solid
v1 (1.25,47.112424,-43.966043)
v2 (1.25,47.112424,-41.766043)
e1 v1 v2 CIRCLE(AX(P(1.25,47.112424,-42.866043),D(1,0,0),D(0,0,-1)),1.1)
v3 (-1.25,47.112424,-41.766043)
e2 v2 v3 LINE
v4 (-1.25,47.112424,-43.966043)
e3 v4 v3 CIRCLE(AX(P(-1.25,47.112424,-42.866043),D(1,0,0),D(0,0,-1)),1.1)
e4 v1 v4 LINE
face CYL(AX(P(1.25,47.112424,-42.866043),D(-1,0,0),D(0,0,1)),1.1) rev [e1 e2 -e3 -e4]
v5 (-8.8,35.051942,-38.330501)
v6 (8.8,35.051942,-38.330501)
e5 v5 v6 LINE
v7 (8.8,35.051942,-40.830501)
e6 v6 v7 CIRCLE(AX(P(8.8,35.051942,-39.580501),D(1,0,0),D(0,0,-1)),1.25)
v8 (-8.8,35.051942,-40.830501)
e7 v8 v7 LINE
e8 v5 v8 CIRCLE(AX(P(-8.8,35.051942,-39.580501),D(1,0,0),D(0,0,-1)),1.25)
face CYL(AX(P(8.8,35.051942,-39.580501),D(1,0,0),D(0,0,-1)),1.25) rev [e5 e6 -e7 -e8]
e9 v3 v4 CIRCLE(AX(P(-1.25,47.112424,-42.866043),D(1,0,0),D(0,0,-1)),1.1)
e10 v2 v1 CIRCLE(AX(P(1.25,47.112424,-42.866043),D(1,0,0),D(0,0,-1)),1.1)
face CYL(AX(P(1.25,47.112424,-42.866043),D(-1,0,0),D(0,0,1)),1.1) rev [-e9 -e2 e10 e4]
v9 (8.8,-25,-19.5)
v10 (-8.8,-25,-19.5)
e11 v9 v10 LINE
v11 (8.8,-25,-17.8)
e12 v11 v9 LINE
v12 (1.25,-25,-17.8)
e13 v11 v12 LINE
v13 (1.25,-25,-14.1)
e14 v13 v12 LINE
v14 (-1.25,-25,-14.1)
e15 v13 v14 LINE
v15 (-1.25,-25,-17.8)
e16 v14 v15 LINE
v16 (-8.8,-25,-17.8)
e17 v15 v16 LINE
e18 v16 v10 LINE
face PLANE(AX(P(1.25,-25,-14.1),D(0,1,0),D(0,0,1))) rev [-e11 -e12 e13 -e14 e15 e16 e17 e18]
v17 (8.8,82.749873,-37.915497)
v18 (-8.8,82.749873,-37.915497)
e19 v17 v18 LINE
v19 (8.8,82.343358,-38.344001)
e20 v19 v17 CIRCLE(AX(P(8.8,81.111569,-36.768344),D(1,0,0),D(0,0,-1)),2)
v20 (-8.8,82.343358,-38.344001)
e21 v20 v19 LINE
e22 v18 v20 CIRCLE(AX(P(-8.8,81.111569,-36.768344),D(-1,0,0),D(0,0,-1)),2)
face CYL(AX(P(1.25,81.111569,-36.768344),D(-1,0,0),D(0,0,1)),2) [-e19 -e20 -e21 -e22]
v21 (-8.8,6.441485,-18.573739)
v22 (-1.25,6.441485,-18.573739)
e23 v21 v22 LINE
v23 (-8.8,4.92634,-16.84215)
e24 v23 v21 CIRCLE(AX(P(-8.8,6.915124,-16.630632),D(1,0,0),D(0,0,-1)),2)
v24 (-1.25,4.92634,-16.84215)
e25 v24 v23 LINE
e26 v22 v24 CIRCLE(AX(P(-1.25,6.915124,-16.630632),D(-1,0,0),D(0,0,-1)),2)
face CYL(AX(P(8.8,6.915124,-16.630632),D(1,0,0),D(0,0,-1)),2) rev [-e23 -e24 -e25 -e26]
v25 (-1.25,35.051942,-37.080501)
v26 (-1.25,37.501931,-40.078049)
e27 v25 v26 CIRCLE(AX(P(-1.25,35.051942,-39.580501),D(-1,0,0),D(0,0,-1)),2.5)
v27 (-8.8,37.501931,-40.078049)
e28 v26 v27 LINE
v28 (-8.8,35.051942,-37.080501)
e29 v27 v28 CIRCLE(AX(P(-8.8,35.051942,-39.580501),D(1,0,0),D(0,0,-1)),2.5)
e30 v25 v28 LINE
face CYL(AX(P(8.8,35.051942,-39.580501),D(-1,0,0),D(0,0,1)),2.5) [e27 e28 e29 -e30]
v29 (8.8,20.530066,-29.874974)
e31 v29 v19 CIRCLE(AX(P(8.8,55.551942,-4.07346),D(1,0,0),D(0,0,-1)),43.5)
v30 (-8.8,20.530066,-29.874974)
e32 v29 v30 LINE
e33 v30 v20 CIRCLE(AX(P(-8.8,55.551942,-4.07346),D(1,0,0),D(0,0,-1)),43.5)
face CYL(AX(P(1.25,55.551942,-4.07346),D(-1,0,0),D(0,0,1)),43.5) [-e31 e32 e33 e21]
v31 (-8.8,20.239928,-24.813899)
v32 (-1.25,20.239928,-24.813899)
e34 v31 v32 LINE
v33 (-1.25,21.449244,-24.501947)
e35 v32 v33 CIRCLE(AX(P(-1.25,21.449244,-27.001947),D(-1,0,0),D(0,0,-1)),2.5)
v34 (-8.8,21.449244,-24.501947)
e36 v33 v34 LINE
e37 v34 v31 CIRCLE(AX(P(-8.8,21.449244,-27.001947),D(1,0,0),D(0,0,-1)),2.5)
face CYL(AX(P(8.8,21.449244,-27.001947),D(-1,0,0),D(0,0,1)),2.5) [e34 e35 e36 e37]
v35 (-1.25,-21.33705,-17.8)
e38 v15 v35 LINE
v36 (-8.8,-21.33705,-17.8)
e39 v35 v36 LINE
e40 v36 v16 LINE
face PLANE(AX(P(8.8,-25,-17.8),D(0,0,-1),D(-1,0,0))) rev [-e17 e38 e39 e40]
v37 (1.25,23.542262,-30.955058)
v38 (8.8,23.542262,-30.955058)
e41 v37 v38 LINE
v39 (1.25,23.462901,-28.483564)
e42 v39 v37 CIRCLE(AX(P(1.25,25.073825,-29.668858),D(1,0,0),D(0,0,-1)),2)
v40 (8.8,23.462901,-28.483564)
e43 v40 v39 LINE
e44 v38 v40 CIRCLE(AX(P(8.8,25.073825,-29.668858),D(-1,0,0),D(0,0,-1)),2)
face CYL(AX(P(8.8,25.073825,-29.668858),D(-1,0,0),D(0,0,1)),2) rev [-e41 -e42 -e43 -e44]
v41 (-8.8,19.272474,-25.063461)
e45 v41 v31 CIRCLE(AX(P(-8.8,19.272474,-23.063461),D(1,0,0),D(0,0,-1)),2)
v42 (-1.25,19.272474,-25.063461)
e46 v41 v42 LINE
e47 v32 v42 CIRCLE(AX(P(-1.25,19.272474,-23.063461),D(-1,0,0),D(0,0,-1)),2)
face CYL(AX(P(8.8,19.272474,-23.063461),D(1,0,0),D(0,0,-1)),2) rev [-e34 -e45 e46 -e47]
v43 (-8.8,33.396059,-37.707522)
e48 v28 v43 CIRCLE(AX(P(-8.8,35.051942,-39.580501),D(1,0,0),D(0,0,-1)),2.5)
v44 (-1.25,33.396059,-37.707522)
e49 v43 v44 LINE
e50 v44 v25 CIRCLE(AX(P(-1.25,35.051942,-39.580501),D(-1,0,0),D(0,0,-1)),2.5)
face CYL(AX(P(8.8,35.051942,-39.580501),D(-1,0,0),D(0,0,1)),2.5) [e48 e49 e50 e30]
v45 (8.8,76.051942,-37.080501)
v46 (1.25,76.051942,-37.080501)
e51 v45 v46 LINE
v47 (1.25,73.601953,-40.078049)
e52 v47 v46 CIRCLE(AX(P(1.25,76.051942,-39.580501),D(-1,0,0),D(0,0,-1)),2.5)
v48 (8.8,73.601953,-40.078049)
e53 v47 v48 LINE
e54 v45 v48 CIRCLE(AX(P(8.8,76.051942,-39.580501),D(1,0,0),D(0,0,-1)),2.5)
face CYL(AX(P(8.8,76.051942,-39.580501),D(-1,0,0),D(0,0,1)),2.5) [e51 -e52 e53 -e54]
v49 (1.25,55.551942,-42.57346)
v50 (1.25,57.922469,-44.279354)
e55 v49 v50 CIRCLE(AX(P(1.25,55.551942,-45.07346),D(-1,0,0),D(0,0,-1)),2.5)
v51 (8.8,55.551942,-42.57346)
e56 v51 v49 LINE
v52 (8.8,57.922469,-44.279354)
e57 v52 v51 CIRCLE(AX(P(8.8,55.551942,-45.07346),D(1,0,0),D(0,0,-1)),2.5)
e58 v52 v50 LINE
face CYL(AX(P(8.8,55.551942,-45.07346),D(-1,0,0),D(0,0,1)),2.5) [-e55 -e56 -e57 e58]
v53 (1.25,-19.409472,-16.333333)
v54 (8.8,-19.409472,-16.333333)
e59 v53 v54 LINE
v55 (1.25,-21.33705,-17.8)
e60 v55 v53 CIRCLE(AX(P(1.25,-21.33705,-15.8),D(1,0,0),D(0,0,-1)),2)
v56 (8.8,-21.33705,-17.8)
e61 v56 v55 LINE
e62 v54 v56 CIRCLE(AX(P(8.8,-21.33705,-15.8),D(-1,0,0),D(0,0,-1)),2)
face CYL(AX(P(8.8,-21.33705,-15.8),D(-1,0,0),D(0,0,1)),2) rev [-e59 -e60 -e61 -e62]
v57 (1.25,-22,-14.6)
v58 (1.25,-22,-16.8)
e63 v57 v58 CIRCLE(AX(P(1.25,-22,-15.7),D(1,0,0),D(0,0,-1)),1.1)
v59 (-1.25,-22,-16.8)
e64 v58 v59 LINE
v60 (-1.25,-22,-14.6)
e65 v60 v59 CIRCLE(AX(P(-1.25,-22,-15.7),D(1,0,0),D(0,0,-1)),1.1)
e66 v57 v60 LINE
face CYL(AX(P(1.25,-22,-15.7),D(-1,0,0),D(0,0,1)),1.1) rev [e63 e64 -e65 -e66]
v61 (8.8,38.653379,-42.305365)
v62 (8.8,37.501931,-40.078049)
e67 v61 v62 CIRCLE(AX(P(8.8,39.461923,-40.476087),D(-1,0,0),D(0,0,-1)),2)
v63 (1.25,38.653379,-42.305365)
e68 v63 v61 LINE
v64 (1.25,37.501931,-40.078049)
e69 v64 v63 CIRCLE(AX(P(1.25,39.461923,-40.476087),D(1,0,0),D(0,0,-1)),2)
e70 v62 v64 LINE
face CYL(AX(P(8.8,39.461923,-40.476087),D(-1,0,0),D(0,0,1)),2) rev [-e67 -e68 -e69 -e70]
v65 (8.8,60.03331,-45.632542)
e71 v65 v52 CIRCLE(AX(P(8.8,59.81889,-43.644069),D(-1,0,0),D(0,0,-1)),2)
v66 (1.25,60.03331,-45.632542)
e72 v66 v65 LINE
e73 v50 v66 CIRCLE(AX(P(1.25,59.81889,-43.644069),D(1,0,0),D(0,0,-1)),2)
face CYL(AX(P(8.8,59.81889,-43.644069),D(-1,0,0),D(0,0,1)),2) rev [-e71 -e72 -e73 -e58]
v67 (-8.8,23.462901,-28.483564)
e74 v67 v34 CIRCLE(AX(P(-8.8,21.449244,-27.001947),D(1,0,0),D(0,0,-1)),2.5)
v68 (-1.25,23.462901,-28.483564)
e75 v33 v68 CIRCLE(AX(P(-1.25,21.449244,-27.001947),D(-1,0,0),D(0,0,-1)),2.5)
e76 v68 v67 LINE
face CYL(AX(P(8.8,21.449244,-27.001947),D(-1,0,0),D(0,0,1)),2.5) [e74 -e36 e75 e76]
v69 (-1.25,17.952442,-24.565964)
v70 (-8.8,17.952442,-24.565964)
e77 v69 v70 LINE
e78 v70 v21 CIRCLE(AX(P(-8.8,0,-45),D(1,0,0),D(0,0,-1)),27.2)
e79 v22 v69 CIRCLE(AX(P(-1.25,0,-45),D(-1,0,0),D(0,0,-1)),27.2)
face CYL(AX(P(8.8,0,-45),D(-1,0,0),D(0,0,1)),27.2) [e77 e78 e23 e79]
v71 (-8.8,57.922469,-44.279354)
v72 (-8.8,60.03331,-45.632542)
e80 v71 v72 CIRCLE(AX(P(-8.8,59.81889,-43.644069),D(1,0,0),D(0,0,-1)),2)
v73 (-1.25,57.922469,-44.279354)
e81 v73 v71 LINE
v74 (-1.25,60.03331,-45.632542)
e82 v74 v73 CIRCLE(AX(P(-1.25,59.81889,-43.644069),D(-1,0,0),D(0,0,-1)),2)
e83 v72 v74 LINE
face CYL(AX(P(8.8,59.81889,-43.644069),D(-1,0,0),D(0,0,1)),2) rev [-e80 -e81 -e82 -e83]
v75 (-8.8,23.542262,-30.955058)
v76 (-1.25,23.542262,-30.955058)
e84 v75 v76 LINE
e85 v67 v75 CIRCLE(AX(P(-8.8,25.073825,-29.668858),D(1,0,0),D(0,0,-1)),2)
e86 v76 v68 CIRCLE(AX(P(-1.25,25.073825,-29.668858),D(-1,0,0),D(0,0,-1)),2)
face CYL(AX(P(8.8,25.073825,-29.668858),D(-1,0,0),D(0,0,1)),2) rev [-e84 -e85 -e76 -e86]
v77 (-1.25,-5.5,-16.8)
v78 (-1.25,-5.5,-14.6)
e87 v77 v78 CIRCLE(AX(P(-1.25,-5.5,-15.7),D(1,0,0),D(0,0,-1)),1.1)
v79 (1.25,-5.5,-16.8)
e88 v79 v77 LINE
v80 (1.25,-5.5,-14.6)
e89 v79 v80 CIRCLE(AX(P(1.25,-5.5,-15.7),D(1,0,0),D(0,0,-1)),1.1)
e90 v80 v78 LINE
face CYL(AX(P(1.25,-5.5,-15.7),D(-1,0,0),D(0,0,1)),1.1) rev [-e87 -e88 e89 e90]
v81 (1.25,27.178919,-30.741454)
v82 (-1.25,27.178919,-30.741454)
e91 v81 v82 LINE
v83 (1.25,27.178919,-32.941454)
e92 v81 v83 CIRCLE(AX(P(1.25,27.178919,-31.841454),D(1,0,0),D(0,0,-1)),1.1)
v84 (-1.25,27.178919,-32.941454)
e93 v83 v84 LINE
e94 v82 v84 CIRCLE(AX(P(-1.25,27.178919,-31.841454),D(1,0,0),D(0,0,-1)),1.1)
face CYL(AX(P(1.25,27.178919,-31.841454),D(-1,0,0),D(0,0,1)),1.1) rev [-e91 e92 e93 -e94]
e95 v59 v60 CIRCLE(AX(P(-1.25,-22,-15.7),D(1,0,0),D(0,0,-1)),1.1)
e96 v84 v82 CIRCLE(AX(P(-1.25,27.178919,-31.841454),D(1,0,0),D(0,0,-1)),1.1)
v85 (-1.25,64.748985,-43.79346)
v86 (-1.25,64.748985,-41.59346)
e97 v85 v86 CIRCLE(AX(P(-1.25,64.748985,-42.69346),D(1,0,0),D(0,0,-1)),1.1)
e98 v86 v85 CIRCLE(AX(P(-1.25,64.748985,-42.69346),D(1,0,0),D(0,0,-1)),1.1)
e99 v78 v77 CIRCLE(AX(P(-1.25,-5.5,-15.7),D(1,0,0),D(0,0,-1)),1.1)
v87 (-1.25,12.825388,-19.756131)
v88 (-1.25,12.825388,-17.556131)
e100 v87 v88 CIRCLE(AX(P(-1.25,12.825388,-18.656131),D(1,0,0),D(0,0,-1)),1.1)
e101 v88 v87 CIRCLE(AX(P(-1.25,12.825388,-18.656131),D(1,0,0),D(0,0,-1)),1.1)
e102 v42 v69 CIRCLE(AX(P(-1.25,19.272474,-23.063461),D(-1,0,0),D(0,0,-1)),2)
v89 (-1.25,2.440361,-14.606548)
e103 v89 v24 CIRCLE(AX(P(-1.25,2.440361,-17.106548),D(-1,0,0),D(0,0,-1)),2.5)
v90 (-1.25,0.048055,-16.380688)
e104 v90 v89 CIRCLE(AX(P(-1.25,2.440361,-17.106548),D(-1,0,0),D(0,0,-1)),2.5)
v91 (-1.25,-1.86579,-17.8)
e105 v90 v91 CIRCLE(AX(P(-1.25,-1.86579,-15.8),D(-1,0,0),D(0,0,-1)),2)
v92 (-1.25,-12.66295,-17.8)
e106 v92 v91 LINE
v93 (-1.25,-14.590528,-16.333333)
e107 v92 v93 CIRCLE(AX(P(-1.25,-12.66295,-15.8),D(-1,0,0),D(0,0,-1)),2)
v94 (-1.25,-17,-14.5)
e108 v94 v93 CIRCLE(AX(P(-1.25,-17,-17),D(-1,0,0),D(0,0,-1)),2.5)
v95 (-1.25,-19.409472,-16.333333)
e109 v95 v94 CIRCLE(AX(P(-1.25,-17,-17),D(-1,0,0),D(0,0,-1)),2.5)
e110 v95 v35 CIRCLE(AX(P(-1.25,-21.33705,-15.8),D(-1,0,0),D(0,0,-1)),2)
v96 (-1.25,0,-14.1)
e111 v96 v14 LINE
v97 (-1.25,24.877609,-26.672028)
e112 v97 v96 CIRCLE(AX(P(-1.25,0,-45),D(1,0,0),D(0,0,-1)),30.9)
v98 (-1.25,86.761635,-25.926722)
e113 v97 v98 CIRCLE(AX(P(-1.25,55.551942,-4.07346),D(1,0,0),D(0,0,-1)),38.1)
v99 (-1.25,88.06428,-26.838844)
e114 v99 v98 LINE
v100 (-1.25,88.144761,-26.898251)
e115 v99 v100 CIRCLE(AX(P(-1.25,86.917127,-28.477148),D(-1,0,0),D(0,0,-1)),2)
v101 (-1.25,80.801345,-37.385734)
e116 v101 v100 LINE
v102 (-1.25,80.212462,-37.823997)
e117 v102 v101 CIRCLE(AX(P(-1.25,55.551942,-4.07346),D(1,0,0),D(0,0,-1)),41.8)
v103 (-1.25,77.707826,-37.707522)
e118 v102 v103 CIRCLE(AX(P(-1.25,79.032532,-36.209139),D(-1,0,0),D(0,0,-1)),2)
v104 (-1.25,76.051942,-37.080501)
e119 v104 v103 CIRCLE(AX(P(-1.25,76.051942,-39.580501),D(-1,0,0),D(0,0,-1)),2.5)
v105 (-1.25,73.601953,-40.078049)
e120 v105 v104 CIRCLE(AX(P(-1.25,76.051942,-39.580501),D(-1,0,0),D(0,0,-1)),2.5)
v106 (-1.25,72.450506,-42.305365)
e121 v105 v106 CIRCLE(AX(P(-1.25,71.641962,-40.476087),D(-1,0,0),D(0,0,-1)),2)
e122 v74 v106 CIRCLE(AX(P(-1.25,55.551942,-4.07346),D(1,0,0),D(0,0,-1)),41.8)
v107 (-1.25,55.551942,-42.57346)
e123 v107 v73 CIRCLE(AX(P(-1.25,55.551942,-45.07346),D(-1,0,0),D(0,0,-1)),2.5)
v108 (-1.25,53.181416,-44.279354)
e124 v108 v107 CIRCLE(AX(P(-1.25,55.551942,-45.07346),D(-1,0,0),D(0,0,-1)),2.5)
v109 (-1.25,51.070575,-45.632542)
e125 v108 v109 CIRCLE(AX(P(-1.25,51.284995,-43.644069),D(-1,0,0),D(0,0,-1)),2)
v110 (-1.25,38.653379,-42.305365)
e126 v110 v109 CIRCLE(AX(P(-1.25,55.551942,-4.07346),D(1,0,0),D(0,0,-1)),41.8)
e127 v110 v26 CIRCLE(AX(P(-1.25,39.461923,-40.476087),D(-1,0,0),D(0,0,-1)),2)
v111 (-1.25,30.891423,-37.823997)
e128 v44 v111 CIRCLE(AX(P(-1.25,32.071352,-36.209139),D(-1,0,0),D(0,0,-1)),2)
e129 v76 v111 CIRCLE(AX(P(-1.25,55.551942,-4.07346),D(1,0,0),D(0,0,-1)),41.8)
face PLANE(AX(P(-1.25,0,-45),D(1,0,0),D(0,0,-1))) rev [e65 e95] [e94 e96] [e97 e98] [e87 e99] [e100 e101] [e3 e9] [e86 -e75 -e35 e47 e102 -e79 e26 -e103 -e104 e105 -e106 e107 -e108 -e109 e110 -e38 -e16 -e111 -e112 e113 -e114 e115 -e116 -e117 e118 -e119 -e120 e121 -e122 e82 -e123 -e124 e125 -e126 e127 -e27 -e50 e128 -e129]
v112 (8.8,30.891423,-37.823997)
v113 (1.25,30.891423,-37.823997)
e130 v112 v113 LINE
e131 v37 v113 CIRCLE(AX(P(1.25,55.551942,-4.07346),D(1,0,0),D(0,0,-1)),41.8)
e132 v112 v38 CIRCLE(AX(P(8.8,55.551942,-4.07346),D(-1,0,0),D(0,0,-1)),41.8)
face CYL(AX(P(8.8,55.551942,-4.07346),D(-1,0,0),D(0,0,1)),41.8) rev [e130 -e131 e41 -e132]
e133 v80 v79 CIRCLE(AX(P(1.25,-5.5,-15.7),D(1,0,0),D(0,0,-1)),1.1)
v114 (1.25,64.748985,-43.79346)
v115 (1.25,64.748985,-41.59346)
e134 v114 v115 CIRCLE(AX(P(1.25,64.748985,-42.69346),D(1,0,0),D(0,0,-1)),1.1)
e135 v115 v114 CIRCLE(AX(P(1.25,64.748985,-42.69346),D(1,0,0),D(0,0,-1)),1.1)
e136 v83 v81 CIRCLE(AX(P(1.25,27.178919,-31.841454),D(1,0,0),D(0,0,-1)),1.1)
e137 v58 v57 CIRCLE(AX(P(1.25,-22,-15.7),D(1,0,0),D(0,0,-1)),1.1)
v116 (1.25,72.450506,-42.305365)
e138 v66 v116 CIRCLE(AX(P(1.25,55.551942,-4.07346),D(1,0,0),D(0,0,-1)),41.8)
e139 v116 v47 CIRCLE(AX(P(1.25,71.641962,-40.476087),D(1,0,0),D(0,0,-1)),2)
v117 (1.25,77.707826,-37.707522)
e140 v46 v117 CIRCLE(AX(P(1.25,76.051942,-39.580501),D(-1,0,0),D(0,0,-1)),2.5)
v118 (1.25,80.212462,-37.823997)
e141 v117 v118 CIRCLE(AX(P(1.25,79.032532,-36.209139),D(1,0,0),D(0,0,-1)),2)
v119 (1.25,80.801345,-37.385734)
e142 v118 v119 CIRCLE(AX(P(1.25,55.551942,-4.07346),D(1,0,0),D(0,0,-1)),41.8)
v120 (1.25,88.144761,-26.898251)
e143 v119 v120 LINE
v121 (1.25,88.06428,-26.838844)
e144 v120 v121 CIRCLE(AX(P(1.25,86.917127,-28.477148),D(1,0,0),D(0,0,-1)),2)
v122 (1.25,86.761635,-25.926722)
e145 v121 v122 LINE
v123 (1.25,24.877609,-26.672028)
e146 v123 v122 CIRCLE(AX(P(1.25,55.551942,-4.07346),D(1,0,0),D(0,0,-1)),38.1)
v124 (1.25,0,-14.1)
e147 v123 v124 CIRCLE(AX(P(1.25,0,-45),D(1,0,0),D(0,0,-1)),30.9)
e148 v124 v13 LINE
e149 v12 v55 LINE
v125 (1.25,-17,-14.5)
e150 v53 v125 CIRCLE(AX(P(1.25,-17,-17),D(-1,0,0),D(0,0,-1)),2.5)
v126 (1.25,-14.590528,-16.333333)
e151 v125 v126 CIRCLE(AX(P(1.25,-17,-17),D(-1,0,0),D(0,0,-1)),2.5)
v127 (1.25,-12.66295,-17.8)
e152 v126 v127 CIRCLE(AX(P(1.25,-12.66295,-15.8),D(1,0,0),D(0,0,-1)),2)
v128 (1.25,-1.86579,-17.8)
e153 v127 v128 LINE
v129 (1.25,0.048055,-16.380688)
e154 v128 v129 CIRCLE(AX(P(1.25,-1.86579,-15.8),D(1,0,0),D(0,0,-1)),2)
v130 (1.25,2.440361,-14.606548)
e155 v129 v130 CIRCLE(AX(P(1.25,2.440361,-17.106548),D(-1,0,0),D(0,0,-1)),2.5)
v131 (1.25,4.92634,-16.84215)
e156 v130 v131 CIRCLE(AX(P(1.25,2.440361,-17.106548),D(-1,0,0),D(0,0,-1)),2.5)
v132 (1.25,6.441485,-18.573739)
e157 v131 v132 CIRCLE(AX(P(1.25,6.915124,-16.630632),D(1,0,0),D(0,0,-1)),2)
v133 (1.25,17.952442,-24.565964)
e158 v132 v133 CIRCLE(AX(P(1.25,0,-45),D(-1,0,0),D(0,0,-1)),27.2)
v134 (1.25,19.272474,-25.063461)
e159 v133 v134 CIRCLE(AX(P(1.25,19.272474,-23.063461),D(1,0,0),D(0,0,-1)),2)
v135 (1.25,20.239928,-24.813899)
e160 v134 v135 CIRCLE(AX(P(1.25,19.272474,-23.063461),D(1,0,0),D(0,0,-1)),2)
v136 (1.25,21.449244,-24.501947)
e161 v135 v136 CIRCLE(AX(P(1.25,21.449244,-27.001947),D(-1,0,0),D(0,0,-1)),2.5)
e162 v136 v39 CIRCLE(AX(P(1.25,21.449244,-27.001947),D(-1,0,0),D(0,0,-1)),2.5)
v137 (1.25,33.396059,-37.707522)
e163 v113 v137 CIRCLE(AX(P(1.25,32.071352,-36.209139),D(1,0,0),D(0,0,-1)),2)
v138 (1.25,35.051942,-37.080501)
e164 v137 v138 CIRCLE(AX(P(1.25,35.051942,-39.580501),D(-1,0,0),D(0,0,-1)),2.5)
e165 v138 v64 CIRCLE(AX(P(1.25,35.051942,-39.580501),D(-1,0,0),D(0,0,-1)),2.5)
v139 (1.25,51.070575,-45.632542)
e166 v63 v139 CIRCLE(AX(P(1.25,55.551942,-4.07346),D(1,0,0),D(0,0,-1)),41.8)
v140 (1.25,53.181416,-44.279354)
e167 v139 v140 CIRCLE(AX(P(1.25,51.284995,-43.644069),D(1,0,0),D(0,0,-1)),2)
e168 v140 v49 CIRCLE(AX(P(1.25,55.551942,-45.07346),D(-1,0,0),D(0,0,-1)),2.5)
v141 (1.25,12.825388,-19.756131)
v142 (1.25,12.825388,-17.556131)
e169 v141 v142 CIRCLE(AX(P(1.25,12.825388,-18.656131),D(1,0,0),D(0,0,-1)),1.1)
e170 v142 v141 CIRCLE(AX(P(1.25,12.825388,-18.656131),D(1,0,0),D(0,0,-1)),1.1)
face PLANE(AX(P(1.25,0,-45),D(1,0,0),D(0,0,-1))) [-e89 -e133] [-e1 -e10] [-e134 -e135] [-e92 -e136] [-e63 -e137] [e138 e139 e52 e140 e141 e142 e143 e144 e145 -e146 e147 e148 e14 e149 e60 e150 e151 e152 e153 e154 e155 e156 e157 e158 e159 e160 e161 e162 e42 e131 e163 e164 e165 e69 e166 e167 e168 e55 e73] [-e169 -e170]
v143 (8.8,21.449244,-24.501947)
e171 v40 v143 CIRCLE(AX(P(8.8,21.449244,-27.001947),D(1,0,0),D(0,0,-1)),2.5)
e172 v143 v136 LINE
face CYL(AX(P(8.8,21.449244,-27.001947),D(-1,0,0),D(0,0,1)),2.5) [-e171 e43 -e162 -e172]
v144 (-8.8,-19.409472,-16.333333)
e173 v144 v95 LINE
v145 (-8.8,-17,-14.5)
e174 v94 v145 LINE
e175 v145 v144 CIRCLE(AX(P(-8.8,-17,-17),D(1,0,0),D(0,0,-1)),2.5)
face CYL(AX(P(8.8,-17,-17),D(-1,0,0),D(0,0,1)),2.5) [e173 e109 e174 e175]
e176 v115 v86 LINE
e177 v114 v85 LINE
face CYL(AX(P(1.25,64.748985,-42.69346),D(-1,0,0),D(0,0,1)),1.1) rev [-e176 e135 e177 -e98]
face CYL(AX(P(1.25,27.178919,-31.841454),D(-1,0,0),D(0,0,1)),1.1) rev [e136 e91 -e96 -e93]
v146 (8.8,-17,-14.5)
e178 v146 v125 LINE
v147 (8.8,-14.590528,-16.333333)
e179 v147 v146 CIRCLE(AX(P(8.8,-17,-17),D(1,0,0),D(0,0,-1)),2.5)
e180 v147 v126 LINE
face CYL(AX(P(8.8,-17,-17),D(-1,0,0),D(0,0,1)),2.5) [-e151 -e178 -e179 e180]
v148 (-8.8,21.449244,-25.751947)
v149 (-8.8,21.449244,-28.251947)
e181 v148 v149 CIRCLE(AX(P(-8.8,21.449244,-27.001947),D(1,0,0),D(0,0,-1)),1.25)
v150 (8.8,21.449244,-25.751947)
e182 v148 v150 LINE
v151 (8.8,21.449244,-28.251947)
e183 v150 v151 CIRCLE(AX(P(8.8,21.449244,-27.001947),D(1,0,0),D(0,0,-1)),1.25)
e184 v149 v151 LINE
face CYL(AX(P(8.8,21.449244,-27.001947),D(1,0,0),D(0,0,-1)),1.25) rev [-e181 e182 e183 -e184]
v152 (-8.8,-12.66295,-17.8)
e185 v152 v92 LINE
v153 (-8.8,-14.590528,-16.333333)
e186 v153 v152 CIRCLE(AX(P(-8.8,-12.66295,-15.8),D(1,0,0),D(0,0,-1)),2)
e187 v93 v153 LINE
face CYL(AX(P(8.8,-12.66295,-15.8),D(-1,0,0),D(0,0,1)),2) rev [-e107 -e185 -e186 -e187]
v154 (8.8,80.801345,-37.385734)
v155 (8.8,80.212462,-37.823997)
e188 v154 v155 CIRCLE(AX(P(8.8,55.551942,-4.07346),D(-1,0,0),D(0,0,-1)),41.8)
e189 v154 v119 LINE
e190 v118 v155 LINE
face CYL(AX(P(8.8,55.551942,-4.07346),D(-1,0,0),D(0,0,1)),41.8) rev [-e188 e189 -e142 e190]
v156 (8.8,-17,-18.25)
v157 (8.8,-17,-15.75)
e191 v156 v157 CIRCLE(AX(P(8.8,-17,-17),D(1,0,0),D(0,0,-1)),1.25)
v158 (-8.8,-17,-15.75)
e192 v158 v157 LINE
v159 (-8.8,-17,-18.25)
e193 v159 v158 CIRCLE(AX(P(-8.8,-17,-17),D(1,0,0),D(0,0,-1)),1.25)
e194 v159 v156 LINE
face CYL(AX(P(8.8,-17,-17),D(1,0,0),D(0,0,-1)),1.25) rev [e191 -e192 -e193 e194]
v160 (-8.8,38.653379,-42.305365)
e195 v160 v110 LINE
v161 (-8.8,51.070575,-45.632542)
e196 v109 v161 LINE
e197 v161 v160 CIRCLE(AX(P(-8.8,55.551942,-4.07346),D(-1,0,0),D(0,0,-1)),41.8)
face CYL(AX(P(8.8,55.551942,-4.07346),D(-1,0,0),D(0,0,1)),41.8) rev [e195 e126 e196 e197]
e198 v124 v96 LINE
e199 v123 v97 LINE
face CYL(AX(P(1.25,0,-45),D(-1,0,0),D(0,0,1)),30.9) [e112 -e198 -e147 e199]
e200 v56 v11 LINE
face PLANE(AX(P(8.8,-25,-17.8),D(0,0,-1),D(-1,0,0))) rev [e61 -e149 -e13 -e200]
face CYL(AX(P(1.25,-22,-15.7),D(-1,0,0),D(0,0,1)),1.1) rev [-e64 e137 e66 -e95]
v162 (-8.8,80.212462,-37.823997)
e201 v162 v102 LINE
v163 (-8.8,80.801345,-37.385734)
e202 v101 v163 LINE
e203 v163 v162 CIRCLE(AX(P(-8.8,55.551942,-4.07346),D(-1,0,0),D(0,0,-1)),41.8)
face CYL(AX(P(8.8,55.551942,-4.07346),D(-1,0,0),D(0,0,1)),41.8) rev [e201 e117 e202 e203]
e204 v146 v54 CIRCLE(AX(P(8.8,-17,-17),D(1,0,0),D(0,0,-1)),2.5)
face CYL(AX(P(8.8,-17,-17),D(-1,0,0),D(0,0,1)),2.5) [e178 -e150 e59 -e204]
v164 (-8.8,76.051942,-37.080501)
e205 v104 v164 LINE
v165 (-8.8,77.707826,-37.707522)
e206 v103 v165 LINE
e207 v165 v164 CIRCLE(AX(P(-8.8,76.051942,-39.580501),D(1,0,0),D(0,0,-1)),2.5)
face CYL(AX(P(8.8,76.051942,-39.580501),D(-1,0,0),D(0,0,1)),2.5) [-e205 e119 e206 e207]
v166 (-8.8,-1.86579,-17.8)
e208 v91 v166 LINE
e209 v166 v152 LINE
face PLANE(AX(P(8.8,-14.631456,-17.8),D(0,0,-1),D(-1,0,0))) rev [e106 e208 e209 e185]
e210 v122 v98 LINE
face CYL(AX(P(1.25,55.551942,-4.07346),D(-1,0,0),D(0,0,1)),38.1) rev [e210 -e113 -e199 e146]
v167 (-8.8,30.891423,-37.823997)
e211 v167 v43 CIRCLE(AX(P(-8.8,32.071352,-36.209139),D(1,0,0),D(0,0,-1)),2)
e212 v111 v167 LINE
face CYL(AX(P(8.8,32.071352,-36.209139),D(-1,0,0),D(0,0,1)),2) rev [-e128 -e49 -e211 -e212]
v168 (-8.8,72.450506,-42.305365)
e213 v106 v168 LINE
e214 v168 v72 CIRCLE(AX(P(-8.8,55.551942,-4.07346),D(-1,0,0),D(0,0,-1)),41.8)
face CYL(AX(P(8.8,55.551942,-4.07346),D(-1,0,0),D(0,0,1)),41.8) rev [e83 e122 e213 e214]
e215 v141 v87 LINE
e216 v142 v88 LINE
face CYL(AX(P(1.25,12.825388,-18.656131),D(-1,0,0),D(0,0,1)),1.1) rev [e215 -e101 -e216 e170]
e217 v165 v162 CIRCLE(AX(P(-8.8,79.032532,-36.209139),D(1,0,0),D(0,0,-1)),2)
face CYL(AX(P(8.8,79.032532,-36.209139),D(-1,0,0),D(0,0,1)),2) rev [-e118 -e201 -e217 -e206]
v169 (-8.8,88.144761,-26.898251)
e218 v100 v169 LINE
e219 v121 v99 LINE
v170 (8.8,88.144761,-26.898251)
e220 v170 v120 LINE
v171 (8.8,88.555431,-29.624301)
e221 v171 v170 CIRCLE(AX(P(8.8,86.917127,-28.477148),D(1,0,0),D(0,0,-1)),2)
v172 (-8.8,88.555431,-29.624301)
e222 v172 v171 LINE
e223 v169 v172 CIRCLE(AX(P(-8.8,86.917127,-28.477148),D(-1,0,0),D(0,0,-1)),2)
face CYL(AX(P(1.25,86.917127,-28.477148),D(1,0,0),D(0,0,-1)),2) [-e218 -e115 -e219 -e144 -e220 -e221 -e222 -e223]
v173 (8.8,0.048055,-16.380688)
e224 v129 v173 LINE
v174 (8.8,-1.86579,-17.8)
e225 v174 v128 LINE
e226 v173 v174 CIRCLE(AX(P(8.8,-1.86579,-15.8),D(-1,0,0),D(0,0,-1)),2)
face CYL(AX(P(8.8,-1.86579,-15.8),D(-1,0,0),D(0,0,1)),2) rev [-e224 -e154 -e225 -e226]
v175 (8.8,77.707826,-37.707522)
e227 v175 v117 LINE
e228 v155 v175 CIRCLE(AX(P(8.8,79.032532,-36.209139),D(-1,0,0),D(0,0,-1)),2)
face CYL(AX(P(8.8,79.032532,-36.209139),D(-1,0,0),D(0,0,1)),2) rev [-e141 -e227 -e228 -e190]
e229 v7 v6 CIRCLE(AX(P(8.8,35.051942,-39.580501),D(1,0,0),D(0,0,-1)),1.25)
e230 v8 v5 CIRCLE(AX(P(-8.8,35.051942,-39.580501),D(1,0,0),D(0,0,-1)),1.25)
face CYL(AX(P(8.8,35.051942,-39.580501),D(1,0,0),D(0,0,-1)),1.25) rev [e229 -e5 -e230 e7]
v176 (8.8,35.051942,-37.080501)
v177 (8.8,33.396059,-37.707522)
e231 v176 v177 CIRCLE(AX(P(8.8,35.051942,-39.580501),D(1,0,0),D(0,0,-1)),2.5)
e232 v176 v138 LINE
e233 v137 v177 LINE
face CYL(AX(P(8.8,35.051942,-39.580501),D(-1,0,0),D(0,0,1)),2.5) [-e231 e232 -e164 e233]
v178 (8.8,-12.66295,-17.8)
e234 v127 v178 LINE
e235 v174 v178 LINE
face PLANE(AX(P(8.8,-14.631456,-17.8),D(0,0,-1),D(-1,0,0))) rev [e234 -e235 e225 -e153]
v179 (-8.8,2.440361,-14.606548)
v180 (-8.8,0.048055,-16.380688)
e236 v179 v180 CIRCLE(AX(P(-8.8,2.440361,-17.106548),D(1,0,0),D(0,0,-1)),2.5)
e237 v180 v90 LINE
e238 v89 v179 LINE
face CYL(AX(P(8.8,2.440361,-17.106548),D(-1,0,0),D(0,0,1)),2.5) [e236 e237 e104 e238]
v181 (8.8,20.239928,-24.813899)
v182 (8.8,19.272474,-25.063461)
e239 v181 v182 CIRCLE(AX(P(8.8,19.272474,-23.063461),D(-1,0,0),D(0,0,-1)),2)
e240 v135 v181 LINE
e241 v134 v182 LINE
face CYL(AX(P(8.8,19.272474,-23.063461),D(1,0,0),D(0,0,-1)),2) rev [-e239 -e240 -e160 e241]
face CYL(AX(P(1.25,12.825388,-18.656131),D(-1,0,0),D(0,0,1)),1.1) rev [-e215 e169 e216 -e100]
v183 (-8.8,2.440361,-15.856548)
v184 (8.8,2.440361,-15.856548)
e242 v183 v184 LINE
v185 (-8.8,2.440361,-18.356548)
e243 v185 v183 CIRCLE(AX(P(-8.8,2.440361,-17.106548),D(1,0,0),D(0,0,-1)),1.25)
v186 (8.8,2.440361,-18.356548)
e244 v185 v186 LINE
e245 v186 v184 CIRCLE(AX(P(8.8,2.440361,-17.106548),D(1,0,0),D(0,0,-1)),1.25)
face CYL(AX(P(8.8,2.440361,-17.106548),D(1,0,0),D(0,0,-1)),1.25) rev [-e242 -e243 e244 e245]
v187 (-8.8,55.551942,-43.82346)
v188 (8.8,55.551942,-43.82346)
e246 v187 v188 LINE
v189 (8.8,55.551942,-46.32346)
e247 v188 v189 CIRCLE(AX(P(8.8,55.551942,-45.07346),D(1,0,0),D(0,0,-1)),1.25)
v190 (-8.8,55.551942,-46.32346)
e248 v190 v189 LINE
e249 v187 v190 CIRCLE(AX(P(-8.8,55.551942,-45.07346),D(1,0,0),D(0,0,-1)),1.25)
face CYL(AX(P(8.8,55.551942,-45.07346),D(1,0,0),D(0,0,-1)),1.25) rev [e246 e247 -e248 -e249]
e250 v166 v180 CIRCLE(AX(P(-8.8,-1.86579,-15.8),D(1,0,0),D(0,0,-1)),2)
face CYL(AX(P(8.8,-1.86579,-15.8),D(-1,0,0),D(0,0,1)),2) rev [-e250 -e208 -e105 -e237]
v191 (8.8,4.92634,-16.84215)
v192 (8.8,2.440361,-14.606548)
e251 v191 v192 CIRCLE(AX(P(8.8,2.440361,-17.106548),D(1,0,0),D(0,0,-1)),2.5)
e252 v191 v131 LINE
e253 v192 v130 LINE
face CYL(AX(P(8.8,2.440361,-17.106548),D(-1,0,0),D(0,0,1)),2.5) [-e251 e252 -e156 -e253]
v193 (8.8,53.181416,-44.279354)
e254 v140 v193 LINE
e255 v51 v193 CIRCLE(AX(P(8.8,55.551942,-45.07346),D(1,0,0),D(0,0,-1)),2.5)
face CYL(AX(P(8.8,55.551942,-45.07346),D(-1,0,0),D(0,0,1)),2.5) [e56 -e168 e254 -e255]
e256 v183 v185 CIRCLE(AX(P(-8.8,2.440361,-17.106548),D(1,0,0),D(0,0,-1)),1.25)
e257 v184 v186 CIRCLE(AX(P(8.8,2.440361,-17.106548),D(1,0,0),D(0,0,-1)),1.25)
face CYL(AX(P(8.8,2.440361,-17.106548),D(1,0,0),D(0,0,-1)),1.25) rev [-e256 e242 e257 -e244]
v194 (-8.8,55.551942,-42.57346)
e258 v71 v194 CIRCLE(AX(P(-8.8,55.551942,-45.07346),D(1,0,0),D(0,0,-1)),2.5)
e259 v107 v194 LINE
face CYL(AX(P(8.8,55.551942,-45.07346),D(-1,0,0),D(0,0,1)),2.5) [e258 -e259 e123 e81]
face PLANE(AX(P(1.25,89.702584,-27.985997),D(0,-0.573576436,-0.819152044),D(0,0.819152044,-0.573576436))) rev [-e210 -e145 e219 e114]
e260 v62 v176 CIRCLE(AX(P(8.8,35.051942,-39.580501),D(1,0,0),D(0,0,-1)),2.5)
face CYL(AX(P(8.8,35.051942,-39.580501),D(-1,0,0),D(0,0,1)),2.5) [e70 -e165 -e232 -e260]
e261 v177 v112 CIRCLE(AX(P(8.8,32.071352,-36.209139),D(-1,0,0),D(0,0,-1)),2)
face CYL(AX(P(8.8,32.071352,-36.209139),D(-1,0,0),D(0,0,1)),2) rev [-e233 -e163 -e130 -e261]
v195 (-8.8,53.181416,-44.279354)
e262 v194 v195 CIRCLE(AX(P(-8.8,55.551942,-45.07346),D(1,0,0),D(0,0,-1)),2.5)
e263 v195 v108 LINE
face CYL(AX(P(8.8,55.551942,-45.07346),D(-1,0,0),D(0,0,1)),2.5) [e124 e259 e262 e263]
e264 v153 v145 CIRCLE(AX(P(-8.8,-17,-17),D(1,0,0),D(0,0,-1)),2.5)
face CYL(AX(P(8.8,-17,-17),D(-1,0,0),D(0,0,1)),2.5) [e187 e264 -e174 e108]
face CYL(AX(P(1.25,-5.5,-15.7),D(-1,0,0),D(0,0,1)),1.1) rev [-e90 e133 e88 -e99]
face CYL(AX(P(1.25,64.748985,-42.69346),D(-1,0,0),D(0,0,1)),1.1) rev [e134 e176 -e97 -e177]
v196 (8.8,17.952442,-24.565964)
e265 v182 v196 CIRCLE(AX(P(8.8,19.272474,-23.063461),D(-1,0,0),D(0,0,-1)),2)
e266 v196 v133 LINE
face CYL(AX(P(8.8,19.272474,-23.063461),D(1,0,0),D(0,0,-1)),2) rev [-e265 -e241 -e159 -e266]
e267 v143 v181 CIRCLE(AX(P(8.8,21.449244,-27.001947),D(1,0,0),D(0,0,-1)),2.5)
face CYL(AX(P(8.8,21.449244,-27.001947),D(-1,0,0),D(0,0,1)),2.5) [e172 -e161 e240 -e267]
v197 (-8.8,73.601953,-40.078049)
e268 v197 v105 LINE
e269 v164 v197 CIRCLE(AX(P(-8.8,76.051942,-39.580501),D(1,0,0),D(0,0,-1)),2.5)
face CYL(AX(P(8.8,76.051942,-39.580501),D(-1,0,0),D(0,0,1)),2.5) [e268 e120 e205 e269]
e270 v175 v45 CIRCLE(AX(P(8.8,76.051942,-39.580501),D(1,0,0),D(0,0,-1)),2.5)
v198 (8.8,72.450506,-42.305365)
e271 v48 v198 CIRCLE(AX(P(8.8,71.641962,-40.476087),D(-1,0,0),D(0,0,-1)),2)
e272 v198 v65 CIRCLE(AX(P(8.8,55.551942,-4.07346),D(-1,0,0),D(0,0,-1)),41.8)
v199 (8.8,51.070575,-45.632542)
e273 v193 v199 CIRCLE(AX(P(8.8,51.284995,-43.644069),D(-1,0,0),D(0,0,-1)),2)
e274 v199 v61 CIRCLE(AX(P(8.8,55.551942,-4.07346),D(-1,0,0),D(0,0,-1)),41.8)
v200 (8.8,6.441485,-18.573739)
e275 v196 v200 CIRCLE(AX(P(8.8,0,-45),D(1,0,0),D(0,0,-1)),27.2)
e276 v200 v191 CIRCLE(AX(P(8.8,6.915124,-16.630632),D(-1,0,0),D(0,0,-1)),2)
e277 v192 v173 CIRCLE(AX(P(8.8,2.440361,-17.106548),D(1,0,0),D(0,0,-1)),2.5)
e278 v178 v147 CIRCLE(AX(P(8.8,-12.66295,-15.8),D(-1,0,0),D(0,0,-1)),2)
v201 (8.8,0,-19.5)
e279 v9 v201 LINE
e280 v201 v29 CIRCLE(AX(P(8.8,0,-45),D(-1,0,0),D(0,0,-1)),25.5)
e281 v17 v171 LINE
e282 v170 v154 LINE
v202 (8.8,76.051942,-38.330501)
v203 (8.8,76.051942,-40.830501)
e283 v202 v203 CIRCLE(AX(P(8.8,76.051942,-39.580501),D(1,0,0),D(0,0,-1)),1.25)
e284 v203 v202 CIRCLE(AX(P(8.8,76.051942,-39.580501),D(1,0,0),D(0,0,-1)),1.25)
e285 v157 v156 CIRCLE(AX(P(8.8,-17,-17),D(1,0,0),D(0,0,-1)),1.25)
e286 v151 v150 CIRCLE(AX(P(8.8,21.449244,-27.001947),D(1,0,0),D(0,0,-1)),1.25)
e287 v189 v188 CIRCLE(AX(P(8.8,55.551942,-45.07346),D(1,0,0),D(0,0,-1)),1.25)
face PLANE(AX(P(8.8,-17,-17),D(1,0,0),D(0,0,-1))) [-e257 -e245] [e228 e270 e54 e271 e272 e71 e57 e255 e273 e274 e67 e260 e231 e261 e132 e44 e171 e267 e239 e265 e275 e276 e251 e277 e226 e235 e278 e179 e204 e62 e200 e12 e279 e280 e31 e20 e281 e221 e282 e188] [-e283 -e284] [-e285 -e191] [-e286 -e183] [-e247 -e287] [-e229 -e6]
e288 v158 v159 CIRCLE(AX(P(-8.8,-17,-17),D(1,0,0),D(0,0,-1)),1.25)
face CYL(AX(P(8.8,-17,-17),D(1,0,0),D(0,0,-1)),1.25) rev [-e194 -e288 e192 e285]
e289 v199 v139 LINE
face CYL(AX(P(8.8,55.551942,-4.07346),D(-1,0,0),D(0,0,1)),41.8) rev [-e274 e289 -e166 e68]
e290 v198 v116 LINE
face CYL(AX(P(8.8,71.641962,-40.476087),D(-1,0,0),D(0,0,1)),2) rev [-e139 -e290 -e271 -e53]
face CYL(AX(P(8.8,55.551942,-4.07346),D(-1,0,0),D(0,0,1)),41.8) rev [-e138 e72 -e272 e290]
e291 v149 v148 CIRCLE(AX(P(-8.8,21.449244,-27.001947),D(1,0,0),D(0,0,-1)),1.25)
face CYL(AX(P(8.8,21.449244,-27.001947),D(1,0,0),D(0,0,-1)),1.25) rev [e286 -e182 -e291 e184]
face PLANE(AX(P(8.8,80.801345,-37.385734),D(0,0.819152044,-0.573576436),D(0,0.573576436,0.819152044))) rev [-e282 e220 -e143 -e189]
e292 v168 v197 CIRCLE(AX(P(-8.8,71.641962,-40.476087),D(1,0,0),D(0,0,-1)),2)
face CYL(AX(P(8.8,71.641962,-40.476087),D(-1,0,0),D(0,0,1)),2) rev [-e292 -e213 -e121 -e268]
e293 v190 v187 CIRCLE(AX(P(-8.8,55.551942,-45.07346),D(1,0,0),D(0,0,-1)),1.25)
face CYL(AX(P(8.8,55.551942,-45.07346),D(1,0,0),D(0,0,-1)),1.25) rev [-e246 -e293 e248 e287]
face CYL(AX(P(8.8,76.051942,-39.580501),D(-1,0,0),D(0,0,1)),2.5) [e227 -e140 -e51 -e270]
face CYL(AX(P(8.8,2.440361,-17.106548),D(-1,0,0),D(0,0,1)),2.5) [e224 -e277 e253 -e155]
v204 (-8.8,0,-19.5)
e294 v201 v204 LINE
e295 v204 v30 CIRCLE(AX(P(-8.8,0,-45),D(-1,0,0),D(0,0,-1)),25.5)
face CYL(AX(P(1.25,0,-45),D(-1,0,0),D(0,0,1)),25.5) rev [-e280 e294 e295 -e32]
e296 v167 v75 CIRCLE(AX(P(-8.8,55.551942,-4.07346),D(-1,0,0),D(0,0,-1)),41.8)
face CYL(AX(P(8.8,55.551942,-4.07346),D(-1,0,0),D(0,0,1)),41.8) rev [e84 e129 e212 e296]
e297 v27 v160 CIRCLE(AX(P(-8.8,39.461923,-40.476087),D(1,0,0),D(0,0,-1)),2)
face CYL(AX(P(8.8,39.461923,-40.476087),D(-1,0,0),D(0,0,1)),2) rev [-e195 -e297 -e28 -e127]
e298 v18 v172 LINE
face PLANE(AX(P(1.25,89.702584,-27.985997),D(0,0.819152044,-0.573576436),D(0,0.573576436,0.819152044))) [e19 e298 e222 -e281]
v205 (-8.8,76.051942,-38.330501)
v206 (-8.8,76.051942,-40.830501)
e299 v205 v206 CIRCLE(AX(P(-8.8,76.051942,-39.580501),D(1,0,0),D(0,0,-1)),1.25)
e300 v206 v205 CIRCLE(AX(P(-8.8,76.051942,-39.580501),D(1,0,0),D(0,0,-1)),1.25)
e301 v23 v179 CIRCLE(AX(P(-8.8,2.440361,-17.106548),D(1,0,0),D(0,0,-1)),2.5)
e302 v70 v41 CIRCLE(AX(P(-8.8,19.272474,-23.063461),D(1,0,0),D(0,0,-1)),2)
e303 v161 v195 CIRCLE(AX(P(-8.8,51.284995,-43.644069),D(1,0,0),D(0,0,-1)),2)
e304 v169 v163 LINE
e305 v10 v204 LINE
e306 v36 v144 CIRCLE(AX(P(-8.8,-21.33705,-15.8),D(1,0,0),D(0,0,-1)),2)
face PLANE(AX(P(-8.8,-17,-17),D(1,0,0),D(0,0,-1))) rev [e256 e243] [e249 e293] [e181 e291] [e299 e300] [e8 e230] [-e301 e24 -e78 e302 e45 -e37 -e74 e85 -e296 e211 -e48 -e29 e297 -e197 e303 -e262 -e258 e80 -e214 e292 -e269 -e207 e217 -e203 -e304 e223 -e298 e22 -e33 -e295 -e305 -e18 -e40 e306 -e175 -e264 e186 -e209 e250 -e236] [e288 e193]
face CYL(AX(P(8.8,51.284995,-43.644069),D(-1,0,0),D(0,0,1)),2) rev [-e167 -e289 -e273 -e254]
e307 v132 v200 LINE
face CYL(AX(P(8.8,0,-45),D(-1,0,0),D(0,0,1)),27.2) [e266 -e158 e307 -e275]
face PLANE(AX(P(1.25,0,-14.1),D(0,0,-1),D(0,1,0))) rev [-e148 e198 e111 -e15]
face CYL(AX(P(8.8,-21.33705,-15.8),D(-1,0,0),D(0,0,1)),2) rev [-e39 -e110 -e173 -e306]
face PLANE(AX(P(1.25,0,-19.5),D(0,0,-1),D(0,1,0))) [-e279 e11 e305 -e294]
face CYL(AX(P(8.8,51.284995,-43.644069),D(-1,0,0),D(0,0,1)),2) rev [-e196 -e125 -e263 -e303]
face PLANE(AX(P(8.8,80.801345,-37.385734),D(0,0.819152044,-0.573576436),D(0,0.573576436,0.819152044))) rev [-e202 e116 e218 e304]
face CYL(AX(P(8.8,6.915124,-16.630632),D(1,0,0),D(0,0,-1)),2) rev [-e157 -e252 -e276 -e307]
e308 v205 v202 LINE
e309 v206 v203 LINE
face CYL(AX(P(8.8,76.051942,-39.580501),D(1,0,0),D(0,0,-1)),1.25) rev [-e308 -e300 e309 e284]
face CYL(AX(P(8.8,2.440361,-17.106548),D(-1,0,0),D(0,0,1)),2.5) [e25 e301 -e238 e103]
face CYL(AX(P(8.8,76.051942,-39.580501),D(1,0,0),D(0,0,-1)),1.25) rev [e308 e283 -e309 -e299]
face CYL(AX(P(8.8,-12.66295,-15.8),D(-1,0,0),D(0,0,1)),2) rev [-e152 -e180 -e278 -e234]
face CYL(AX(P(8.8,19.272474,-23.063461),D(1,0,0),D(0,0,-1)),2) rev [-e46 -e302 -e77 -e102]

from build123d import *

# Parameters (mm, degrees)
SKETCH_3_R         = 1.0999999999999992
SKETCH_3_R_2       = 1.100000000000007
SKETCH_3_R_3       = 1.0999999999999983
EXTRUDE_1_DEPTH    = 1.25
EXTRUDE_2_DEPTH    = 8.8
HOLE_WIZARD_M3_1_D = 2.5
FILLET_R2_1_R      = 2


with BuildPart() as part:
    # 草图3 → 凸台-拉伸1 (new, symmetric)
    with BuildSketch(Plane(origin=(0, 0, 0), x_dir=(0, 0, -1), z_dir=(1, 0, 0))):
        with BuildLine():
            Line((19.5, -3.12e-15), (19.500000000000004, -25.00000000000001))
            Line((19.500000000000004, -25.00000000000001), (14.100000000000005, -25.00000000000001))
            Line((14.100000000000005, -25.00000000000001), (14.100000000000001, 0))
            ThreePointArc((14.100000000000001, 0), (17.421526991333195, 13.936923136411288), (26.672027605840533, 24.877608967079777))
            ThreePointArc((26.672027605840533, 24.877608967079777), (42.17069683857236, 56.010769758457506), (25.926721927337365, 86.76163524108378))
            Line((25.926721927337365, 86.76163524108378), (27.985996640623934, 89.70258431819843))
            Line((27.985996640623934, 89.70258431819843), (38.157154957885716, 82.58066259212733))
            ThreePointArc((38.157154957885716, 82.58066259212733), (47.19107481579925, 49.796834454639864), (29.874974237829562, 20.530065652444478))
            ThreePointArc((29.874974237829562, 20.530065652444478), (22.241065963721567, 11.501344335873394), (19.5, -3.12e-15))
        make_face()
        with Locations((15.700000000000003, -22.000000000000014)):
            Circle(SKETCH_3_R, mode=Mode.SUBTRACT)
        with Locations((15.700000000000003, -5.5000000000000115)):
            Circle(SKETCH_3_R, mode=Mode.SUBTRACT)
        with Locations((18.656131284605202, 12.825388146408793)):
            Circle(SKETCH_3_R, mode=Mode.SUBTRACT)
        with Locations((42.69345970236235, 64.74898535672597)):
            Circle(SKETCH_3_R_2, mode=Mode.SUBTRACT)
        with Locations((31.841454389394453, 27.178918703364943)):
            Circle(SKETCH_3_R, mode=Mode.SUBTRACT)
        with Locations((42.86604311676676, 47.112423881836435)):
            Circle(SKETCH_3_R_3, mode=Mode.SUBTRACT)
    extrude(amount=EXTRUDE_1_DEPTH, both=True)

    # 草图4 → 凸台-拉伸2 (add, symmetric)
    with BuildSketch(Plane(origin=(0, 0, 0), x_dir=(0, 0, -1), z_dir=(1, 0, 0))):
        with BuildLine():
            Line((19.500000000000004, 3.12e-15), (19.500000000000004, -25.00000000000001))
            Line((19.500000000000004, -25.00000000000001), (17.800000000000004, -25.00000000000001))
            Line((17.800000000000004, -25.00000000000001), (17.800000000000004, -19.368543856465415))
            ThreePointArc((17.800000000000004, -19.368543856465415), (14.5, -17.00000000000001), (17.800000000000004, -14.63145614353461))
            Line((17.800000000000004, -14.63145614353461), (17.800000000000004, 0.03846051745544626))
            ThreePointArc((17.800000000000004, 0.03846051745544626), (14.616062942086879, 2.658264256715171), (18.206575944742145, 4.685341758626529))
            ThreePointArc((18.206575944742145, 4.685341758626529), (20.873305337552384, 12.559562279992942), (25.793916032971335, 19.2604864593666))
            ThreePointArc((25.793916032971335, 19.2604864593666), (25.390331087301867, 23.36044674604562), (29.363264344403504, 22.270329093985996))
            ThreePointArc((29.363264344403504, 22.270329093985996), (34.63201747726785, 27.031519027261), (39.01879216923118, 32.61586294196908))
            ThreePointArc((39.01879216923118, 32.61586294196908), (37.41543774806319, 36.301942353673255), (41.409353369549805, 36.75643639952374))
            ThreePointArc((41.409353369549805, 36.75643639952374), (44.44915924124539, 44.73330626838789), (45.805045068215996, 53.16138115335468))
            ThreePointArc((45.805045068215996, 53.16138115335468), (42.57345970236232, 55.5519423536733), (45.805045068215996, 57.94250355399191))
            ThreePointArc((45.805045068215996, 57.94250355399191), (44.44915924124538, 66.3705784389587), (41.409353369549805, 74.34744830782286))
            ThreePointArc((41.409353369549805, 74.34744830782286), (37.41543774806319, 74.80194235367335), (39.01879216923118, 78.48802176537752))
            ThreePointArc((39.01879216923118, 78.48802176537752), (38.22185794799814, 79.65851608901482), (37.38573446811181, 80.80134531554968))
            Line((37.38573446811181, 80.80134531554968), (26.896201411556945, 88.14619543404935))
            Line((26.896201411556945, 88.14619543404935), (27.985996640623934, 89.70258431819843))
            Line((27.985996640623934, 89.70258431819843), (38.1571549578857, 82.58066259212734))
            ThreePointArc((38.1571549578857, 82.58066259212734), (47.19107481579925, 49.79683445463986), (29.874974237829548, 20.530065652444467))
            ThreePointArc((29.874974237829548, 20.530065652444467), (22.24106596372156, 11.501344335873386), (19.500000000000004, 3.12e-15))
        make_face()
    extrude(amount=EXTRUDE_2_DEPTH, both=True)

    # M3 螺纹孔1 (through all)
    with Locations(Plane(origin=(8.8, 0, 0), x_dir=(0, 0, -1), z_dir=(1, 0, 0))):
        with Locations((39.580501258, 76.051942354), (45.073459702, 55.551942354), (39.580501258, 35.051942354), (27.001946929, 21.449244407), (17.106548453, 2.440360797), (17, -17)):
            Hole(HOLE_WIZARD_M3_1_D / 2)

    # R2 圆角1
    fillet_r2_1_edges = [part.edges().sort_by_distance(p)[0] for p in [
        (0, 82.58066259212734, -38.15715495788571),
        (0, 89.70258431819843, -27.985996640623934),
        (5.025, -19.368543856465415, -17.800000000000004),
        (-5.025, -19.368543856465415, -17.800000000000004),
        (-5.025, -14.63145614353461, -17.800000000000004),
        (5.025, -14.63145614353461, -17.800000000000004),
        (5.025, 0.03846051745544712, -17.800000000000004),
        (-5.025, 0.03846051745544712, -17.800000000000004),
        (-5.025, 4.68534175862653, -18.20657594474214),
        (5.025, 4.68534175862653, -18.20657594474214),
        (-5.025, 19.260486459366604, -25.79391603297133),
        (5.025, 19.260486459366604, -25.79391603297133),
        (-5.025, 22.270329093985993, -29.363264344403504),
        (5.025, 22.270329093985993, -29.363264344403504),
        (-5.025, 32.61586294196907, -39.01879216923119),
        (5.025, 32.61586294196907, -39.01879216923119),
        (-5.025, 36.756436399523736, -41.409353369549805),
        (5.025, 36.756436399523736, -41.409353369549805),
        (-5.025, 53.16138115335468, -45.805045068216),
        (5.025, 53.16138115335468, -45.805045068216),
        (5.025, 57.94250355399191, -45.80504506821599),
        (-5.025, 57.94250355399191, -45.80504506821599),
        (5.025, 74.34744830782286, -41.409353369549805),
        (-5.025, 74.34744830782286, -41.409353369549805),
        (-5.025, 78.48802176537752, -39.01879216923119),
        (5.025, 78.48802176537752, -39.01879216923119),
    ]]
    fillet(fillet_r2_1_edges, radius=FILLET_R2_1_R)


solid = part.part
